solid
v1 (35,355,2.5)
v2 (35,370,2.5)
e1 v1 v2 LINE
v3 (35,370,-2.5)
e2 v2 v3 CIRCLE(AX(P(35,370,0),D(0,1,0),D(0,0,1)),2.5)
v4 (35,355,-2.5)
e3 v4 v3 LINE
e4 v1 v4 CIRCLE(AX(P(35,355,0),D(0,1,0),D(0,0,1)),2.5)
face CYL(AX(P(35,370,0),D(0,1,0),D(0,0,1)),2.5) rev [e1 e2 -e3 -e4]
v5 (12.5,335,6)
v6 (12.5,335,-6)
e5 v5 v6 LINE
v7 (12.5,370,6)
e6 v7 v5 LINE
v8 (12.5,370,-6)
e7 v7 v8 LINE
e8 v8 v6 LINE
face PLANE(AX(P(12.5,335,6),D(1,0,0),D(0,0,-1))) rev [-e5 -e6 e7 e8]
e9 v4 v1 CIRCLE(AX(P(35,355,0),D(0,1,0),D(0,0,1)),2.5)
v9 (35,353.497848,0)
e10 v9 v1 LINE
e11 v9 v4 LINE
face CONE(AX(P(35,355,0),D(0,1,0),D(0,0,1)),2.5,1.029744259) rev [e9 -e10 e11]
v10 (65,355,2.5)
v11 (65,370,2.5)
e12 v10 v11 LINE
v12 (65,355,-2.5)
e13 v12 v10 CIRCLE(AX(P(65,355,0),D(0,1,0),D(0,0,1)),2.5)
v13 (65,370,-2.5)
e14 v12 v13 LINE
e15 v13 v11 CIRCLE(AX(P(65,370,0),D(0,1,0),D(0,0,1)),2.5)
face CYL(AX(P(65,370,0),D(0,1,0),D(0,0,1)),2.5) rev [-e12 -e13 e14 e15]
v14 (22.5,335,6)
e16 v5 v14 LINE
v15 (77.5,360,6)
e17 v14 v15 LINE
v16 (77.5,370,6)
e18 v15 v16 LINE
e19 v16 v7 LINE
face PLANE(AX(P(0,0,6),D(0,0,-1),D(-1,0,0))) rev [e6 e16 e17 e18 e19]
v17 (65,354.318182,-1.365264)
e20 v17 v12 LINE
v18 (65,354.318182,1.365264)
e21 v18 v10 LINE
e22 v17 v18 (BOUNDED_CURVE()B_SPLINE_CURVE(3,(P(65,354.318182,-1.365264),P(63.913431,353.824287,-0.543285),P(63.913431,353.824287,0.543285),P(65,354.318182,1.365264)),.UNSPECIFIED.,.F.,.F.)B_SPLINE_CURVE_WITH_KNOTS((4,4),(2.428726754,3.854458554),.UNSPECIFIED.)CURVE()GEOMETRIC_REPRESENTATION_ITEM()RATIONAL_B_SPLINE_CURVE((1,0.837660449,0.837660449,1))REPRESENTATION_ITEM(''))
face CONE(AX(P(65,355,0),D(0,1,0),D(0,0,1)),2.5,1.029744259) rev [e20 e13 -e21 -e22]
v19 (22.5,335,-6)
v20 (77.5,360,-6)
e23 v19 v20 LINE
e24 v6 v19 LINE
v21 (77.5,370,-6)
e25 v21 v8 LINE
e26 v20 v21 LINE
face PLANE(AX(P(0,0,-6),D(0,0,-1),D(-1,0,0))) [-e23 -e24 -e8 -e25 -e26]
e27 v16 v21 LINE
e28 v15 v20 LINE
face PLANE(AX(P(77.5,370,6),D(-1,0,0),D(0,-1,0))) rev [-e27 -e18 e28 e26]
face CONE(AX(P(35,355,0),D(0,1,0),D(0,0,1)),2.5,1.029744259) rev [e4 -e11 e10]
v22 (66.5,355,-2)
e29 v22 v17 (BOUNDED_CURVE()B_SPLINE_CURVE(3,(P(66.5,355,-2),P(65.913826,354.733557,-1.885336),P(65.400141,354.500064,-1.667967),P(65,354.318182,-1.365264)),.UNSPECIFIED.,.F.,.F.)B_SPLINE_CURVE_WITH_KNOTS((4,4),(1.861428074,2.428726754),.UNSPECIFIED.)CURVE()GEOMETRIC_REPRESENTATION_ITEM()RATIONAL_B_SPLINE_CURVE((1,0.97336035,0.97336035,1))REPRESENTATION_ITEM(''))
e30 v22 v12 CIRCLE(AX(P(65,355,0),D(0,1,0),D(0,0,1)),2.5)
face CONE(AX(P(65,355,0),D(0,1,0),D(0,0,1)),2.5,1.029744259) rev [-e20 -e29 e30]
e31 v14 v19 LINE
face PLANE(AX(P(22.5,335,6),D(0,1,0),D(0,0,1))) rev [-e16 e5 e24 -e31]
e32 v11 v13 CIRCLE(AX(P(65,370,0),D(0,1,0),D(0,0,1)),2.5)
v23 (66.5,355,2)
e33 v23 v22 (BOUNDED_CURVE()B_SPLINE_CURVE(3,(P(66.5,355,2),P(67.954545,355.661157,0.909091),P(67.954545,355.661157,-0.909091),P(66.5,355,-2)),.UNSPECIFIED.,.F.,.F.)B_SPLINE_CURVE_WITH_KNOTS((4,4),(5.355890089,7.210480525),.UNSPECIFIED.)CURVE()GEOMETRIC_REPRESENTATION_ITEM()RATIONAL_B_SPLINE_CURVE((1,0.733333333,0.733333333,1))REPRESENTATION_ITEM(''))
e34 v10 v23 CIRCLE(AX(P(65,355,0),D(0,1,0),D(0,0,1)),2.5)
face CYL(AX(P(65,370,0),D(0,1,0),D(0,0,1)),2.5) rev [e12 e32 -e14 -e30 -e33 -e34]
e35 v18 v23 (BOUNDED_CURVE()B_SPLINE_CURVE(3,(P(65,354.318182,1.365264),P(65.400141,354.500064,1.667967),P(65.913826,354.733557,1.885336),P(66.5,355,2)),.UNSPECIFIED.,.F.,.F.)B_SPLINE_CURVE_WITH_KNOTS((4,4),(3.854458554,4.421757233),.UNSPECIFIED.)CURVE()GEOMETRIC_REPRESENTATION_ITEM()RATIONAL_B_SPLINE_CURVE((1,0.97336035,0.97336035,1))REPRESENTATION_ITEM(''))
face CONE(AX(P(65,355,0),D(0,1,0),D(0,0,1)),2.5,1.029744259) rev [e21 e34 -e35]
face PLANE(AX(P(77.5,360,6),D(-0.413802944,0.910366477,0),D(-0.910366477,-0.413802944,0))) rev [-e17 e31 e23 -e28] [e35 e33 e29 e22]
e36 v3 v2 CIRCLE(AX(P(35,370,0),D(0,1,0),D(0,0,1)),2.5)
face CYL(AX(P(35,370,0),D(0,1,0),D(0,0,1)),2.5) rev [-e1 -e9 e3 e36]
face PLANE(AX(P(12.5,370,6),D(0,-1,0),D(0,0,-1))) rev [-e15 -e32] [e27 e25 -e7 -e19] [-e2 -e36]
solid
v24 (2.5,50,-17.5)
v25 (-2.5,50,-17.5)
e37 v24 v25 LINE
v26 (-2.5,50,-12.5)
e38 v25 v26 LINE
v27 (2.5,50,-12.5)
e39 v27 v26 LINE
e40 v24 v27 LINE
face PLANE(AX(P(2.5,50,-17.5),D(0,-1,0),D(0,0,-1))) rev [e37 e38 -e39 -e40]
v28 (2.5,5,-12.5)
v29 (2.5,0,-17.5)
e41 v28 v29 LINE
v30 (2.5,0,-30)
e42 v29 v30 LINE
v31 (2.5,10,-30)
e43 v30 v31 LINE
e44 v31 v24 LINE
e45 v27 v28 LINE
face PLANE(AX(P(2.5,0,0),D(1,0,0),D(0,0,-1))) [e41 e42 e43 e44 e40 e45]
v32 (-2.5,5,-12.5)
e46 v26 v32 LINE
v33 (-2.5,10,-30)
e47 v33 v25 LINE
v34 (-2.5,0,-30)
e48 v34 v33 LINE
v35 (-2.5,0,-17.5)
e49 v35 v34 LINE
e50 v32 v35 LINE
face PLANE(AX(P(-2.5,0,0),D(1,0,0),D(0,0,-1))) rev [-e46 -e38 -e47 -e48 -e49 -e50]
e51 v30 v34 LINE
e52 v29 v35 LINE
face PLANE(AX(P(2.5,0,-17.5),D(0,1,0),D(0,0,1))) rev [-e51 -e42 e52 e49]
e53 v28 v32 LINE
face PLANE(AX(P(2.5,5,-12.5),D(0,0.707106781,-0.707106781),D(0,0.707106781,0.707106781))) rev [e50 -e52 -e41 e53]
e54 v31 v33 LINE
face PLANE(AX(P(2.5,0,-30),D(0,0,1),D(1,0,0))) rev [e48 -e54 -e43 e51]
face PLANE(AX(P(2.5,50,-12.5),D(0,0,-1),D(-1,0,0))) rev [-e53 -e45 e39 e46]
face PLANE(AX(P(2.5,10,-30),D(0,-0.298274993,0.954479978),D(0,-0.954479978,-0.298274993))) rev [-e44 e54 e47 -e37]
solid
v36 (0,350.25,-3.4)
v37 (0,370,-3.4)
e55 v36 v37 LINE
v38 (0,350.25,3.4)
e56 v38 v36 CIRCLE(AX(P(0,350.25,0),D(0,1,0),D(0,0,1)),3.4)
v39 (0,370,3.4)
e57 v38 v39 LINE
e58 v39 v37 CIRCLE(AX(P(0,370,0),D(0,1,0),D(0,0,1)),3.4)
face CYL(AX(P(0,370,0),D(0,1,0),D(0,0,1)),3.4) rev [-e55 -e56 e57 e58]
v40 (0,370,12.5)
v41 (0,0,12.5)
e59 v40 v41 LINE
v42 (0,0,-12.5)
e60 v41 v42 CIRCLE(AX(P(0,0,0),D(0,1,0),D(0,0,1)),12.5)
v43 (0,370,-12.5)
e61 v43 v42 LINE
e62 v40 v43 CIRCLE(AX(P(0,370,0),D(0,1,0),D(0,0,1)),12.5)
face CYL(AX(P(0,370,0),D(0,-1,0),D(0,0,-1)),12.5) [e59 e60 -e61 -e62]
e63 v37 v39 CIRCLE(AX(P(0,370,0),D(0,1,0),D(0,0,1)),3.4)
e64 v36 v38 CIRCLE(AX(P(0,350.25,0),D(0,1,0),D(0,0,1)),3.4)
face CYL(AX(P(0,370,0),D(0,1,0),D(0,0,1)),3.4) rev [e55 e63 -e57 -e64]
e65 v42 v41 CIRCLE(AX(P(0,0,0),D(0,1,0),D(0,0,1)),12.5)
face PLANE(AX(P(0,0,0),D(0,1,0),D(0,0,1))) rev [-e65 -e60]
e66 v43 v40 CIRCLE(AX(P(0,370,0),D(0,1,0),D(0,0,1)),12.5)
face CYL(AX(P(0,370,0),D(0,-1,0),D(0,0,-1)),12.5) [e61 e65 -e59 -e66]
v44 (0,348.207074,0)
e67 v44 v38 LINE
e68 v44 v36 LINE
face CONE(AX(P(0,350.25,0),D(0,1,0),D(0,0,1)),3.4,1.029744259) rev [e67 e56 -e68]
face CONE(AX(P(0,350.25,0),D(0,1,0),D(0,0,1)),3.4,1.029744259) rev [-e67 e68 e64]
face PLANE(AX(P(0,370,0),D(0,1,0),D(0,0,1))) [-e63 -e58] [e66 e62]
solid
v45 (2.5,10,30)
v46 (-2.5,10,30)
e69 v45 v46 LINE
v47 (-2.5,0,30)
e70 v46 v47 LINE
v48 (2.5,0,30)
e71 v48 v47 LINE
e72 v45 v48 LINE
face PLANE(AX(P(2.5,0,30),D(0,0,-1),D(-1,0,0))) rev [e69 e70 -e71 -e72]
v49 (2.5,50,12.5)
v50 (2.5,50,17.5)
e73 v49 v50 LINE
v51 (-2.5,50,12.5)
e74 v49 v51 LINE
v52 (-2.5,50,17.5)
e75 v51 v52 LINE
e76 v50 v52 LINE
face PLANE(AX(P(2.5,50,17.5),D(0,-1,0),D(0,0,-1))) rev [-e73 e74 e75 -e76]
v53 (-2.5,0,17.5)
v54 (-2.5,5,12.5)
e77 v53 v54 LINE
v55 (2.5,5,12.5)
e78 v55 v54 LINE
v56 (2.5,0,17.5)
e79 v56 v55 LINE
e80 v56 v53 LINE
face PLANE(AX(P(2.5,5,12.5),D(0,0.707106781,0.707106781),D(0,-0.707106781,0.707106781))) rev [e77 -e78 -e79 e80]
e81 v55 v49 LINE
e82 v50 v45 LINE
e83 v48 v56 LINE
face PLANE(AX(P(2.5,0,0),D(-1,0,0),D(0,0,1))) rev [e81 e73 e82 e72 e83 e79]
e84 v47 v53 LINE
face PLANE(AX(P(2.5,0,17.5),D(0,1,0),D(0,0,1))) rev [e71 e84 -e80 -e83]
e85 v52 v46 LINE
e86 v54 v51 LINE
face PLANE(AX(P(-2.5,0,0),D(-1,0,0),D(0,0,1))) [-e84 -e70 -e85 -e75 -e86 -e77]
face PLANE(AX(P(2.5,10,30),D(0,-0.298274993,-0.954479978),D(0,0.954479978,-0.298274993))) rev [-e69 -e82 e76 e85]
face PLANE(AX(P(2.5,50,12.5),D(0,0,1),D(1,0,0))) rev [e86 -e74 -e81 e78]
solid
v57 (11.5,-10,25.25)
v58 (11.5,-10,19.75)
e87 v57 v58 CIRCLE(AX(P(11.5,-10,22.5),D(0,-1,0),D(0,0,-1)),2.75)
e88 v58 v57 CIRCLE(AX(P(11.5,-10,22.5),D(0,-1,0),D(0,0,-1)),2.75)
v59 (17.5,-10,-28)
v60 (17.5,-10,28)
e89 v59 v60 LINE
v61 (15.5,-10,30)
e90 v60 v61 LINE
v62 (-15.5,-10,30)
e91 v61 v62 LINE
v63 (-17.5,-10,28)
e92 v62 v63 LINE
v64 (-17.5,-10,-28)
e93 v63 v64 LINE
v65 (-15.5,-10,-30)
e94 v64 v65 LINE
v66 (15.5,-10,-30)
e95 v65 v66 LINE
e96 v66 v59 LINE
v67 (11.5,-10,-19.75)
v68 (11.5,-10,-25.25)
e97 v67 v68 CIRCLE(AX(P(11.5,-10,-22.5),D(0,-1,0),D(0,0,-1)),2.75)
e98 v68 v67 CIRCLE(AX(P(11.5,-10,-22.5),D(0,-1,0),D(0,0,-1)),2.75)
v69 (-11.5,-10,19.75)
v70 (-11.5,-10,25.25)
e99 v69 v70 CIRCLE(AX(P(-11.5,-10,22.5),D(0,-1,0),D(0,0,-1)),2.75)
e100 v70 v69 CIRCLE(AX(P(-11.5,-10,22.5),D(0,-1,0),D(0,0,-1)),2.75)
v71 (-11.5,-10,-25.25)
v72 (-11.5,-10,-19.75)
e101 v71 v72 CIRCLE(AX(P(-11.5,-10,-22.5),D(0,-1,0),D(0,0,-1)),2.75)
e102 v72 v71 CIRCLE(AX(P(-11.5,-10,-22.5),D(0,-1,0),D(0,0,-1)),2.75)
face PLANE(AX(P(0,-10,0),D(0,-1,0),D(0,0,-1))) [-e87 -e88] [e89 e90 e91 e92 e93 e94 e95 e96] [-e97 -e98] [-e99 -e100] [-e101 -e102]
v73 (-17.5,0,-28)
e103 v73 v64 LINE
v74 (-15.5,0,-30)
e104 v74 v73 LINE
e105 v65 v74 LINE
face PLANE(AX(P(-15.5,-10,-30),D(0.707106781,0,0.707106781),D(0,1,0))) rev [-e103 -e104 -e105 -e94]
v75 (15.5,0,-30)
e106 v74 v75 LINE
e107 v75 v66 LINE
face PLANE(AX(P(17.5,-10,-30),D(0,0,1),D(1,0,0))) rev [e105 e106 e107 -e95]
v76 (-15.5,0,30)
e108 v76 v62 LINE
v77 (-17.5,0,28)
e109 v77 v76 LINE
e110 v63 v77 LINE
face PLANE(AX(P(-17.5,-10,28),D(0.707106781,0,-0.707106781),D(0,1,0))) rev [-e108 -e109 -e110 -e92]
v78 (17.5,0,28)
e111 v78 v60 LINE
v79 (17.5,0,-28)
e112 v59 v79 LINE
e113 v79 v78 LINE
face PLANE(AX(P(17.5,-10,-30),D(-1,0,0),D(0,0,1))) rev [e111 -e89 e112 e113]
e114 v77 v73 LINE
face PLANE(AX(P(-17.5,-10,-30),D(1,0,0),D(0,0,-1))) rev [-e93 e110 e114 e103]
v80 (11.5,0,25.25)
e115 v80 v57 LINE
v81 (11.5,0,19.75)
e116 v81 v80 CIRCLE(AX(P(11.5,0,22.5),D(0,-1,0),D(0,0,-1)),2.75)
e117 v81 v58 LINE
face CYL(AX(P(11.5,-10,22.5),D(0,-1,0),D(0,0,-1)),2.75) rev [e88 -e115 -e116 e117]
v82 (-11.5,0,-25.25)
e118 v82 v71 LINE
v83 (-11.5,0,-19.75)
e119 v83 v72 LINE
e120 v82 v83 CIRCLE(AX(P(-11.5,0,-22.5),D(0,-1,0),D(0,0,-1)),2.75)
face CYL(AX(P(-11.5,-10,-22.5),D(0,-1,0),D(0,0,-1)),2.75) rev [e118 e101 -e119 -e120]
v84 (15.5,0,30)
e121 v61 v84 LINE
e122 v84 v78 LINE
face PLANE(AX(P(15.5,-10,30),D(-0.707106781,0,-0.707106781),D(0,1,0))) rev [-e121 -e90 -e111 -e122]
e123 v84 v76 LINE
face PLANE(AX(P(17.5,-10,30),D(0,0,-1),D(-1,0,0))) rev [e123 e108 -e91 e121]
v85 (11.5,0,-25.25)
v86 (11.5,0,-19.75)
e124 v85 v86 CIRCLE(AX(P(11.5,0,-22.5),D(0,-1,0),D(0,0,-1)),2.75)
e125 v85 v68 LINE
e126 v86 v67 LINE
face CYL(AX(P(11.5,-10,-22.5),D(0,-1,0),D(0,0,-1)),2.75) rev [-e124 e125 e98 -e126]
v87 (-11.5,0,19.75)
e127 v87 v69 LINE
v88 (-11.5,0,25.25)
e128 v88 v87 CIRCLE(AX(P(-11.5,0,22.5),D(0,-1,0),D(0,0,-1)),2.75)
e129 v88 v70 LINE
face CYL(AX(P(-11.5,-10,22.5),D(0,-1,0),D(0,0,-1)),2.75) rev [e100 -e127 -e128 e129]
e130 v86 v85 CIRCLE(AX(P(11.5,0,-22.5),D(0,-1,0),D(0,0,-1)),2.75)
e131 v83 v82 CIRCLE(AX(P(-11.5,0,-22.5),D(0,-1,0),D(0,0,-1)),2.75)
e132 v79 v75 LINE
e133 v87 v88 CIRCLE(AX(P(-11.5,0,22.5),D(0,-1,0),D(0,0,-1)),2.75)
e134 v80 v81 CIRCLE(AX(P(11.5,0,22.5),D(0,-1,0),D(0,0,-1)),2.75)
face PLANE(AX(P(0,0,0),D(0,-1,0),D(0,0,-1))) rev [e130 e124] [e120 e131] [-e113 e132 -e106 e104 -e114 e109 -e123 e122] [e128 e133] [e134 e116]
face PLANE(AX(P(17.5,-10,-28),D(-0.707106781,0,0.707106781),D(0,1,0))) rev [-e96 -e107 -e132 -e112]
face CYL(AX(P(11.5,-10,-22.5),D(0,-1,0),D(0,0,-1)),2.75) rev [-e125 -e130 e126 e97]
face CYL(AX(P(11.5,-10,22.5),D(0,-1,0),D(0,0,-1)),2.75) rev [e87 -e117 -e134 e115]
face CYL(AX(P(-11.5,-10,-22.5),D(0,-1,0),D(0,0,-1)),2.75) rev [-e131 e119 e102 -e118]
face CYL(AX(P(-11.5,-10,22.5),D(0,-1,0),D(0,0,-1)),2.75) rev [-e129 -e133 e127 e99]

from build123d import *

# Parameters (mm, degrees)
SKETCH_1_R                  = 12.5
EXTRUDE_1_DEPTH             = 370
SKETCH_2_W                  = 35
SKETCH_2_H                  = 60
EXTRUDE_2_DEPTH             = 10
EXTRUDE_3_DEPTH             = 6
HOLE_WIZARD_M6_1_AT_2_COUNT = 2
HOLE_WIZARD_M6_1_AT_2_PITCH = 30
EXTRUDE_4_DEPTH             = 2.5
EXTRUDE_4_2_DEPTH           = 2.5
HOLE_WIZARD_M5_1_AT_2_COUNT = 2
HOLE_WIZARD_M5_1_AT_2_PITCH = 23
HOLE_WIZARD_M5_1_AT_3_COUNT = 2
HOLE_WIZARD_M5_1_AT_3_PITCH = 50.537115074
HOLE_WIZARD_M5_1_AT_4_COUNT = 2
HOLE_WIZARD_M5_1_AT_4_PITCH = 45
CHAMFER_1_SIZE              = 2


with BuildPart() as part:
    # 草图1 → 凸台-拉伸1 (new body)
    with BuildSketch(Plane(origin=(0, 0, 0), x_dir=(1, 0, 0), z_dir=(0, 1, 0))):
        with Locations(Location((0, 0, 0), (0, 0, 270))):
            Circle(SKETCH_1_R)
    extrude(amount=EXTRUDE_1_DEPTH)

    # 草图5 → M8 螺纹孔1 (revolve, cut)
    with BuildSketch(Plane(origin=(0, 370, 0), x_dir=(0, 0, 1), z_dir=(1, 0, 0))):
        Polygon((0, 0), (0, 21.792926105), (3.4, 19.75), (3.4, 0), align=None)
    revolve(axis=Axis((0, 376.35, 0), (0, -1, 0)), mode=Mode.SUBTRACT)


with BuildPart() as body_2:
    # 草图2 → 凸台-拉伸2 (new body)
    with BuildSketch(Plane.XZ):
        Rectangle(SKETCH_2_W, SKETCH_2_H)
    extrude(amount=EXTRUDE_2_DEPTH)

    # 草图10 → M5 间隙孔1 (revolve, cut)
    with BuildSketch(Plane(origin=(11.5, -10, -22.5), x_dir=(0, 0, -1), z_dir=(1, 0, 0))):
        Polygon((0, 0), (0, 16.652366702), (2.75, 15), (2.75, 0), align=None)
    hole_wizard_m5_1 = revolve(axis=Axis((11.5, -16.35, -22.5), (0, 1, 0)), mode=Mode.SUBTRACT)

    # M5 间隙孔1 at 2: M5 间隙孔1 ×2
    with Locations(*[(-i * HOLE_WIZARD_M5_1_AT_2_PITCH, 0, 0) for i in range(1, HOLE_WIZARD_M5_1_AT_2_COUNT)]):
        add(hole_wizard_m5_1, mode=Mode.SUBTRACT)

    # M5 间隙孔1 at 3: M5 间隙孔1 ×2
    with Locations(*[Vector(-0.45511105978910793, 0, 0.8904346821960806) * (i * HOLE_WIZARD_M5_1_AT_3_PITCH) for i in range(1, HOLE_WIZARD_M5_1_AT_3_COUNT)]):
        add(hole_wizard_m5_1, mode=Mode.SUBTRACT)

    # M5 间隙孔1 at 4: M5 间隙孔1 ×2
    with Locations(*[(0, 0, i * HOLE_WIZARD_M5_1_AT_4_PITCH) for i in range(1, HOLE_WIZARD_M5_1_AT_4_COUNT)]):
        add(hole_wizard_m5_1, mode=Mode.SUBTRACT)

    # 倒角1
    chamfer_1_edges = [body_2.edges().sort_by_distance(p)[0] for p in [
        (-17.5, -5, 30),
        (17.5, -5, 30),
        (17.5, -5, -30),
        (-17.5, -5, -30),
    ]]
    chamfer(chamfer_1_edges, length=CHAMFER_1_SIZE)


with BuildPart() as body_3:
    # 草图3 → 凸台-拉伸3 (new, symmetric)
    with BuildSketch(Plane.XY):
        Polygon((12.5, 370), (77.5, 370), (77.5, 360), (22.5, 335), (12.5, 335), align=None)
    extrude(amount=EXTRUDE_3_DEPTH, both=True)

    # 草图7 → M6 螺纹孔1 (revolve, cut)
    with BuildSketch(Plane(origin=(35, 370, 0), x_dir=(0, 0, 1), z_dir=(1, 0, 0))):
        Polygon((0, 0), (0, 16.502151548), (2.5, 15), (2.5, 0), align=None)
    hole_wizard_m6_1 = revolve(axis=Axis((35, 376.35, 0), (0, -1, 0)), mode=Mode.SUBTRACT)

    # M6 螺纹孔1 at 2: M6 螺纹孔1 ×2
    with Locations(*[(i * HOLE_WIZARD_M6_1_AT_2_PITCH, 0, 0) for i in range(1, HOLE_WIZARD_M6_1_AT_2_COUNT)]):
        add(hole_wizard_m6_1, mode=Mode.SUBTRACT)


with BuildPart() as body_4:
    # 草图8 → 凸台-拉伸4 (new, symmetric)
    with BuildSketch(Plane(origin=(0, 0, 0), x_dir=(0, 0, -1), z_dir=(1, 0, 0))):
        Polygon((30, 0), (30, 10), (17.5, 50), (12.5, 50), (12.5, 5), (17.5, 0), align=None)
    extrude(amount=EXTRUDE_4_DEPTH, both=True)


with BuildPart() as body_5:
    # 草图8 → Extrude 4 2 (new, symmetric)
    with BuildSketch(Plane(origin=(0, 0, 0), x_dir=(0, 0, -1), z_dir=(1, 0, 0))):
        Polygon((-12.5, 5), (-17.5, 0), (-30, 0), (-30, 10), (-17.5, 50), (-12.5, 50), align=None)
    extrude(amount=EXTRUDE_4_2_DEPTH, both=True)


solid = Compound([part.part, body_2.part, body_3.part, body_4.part, body_5.part])
